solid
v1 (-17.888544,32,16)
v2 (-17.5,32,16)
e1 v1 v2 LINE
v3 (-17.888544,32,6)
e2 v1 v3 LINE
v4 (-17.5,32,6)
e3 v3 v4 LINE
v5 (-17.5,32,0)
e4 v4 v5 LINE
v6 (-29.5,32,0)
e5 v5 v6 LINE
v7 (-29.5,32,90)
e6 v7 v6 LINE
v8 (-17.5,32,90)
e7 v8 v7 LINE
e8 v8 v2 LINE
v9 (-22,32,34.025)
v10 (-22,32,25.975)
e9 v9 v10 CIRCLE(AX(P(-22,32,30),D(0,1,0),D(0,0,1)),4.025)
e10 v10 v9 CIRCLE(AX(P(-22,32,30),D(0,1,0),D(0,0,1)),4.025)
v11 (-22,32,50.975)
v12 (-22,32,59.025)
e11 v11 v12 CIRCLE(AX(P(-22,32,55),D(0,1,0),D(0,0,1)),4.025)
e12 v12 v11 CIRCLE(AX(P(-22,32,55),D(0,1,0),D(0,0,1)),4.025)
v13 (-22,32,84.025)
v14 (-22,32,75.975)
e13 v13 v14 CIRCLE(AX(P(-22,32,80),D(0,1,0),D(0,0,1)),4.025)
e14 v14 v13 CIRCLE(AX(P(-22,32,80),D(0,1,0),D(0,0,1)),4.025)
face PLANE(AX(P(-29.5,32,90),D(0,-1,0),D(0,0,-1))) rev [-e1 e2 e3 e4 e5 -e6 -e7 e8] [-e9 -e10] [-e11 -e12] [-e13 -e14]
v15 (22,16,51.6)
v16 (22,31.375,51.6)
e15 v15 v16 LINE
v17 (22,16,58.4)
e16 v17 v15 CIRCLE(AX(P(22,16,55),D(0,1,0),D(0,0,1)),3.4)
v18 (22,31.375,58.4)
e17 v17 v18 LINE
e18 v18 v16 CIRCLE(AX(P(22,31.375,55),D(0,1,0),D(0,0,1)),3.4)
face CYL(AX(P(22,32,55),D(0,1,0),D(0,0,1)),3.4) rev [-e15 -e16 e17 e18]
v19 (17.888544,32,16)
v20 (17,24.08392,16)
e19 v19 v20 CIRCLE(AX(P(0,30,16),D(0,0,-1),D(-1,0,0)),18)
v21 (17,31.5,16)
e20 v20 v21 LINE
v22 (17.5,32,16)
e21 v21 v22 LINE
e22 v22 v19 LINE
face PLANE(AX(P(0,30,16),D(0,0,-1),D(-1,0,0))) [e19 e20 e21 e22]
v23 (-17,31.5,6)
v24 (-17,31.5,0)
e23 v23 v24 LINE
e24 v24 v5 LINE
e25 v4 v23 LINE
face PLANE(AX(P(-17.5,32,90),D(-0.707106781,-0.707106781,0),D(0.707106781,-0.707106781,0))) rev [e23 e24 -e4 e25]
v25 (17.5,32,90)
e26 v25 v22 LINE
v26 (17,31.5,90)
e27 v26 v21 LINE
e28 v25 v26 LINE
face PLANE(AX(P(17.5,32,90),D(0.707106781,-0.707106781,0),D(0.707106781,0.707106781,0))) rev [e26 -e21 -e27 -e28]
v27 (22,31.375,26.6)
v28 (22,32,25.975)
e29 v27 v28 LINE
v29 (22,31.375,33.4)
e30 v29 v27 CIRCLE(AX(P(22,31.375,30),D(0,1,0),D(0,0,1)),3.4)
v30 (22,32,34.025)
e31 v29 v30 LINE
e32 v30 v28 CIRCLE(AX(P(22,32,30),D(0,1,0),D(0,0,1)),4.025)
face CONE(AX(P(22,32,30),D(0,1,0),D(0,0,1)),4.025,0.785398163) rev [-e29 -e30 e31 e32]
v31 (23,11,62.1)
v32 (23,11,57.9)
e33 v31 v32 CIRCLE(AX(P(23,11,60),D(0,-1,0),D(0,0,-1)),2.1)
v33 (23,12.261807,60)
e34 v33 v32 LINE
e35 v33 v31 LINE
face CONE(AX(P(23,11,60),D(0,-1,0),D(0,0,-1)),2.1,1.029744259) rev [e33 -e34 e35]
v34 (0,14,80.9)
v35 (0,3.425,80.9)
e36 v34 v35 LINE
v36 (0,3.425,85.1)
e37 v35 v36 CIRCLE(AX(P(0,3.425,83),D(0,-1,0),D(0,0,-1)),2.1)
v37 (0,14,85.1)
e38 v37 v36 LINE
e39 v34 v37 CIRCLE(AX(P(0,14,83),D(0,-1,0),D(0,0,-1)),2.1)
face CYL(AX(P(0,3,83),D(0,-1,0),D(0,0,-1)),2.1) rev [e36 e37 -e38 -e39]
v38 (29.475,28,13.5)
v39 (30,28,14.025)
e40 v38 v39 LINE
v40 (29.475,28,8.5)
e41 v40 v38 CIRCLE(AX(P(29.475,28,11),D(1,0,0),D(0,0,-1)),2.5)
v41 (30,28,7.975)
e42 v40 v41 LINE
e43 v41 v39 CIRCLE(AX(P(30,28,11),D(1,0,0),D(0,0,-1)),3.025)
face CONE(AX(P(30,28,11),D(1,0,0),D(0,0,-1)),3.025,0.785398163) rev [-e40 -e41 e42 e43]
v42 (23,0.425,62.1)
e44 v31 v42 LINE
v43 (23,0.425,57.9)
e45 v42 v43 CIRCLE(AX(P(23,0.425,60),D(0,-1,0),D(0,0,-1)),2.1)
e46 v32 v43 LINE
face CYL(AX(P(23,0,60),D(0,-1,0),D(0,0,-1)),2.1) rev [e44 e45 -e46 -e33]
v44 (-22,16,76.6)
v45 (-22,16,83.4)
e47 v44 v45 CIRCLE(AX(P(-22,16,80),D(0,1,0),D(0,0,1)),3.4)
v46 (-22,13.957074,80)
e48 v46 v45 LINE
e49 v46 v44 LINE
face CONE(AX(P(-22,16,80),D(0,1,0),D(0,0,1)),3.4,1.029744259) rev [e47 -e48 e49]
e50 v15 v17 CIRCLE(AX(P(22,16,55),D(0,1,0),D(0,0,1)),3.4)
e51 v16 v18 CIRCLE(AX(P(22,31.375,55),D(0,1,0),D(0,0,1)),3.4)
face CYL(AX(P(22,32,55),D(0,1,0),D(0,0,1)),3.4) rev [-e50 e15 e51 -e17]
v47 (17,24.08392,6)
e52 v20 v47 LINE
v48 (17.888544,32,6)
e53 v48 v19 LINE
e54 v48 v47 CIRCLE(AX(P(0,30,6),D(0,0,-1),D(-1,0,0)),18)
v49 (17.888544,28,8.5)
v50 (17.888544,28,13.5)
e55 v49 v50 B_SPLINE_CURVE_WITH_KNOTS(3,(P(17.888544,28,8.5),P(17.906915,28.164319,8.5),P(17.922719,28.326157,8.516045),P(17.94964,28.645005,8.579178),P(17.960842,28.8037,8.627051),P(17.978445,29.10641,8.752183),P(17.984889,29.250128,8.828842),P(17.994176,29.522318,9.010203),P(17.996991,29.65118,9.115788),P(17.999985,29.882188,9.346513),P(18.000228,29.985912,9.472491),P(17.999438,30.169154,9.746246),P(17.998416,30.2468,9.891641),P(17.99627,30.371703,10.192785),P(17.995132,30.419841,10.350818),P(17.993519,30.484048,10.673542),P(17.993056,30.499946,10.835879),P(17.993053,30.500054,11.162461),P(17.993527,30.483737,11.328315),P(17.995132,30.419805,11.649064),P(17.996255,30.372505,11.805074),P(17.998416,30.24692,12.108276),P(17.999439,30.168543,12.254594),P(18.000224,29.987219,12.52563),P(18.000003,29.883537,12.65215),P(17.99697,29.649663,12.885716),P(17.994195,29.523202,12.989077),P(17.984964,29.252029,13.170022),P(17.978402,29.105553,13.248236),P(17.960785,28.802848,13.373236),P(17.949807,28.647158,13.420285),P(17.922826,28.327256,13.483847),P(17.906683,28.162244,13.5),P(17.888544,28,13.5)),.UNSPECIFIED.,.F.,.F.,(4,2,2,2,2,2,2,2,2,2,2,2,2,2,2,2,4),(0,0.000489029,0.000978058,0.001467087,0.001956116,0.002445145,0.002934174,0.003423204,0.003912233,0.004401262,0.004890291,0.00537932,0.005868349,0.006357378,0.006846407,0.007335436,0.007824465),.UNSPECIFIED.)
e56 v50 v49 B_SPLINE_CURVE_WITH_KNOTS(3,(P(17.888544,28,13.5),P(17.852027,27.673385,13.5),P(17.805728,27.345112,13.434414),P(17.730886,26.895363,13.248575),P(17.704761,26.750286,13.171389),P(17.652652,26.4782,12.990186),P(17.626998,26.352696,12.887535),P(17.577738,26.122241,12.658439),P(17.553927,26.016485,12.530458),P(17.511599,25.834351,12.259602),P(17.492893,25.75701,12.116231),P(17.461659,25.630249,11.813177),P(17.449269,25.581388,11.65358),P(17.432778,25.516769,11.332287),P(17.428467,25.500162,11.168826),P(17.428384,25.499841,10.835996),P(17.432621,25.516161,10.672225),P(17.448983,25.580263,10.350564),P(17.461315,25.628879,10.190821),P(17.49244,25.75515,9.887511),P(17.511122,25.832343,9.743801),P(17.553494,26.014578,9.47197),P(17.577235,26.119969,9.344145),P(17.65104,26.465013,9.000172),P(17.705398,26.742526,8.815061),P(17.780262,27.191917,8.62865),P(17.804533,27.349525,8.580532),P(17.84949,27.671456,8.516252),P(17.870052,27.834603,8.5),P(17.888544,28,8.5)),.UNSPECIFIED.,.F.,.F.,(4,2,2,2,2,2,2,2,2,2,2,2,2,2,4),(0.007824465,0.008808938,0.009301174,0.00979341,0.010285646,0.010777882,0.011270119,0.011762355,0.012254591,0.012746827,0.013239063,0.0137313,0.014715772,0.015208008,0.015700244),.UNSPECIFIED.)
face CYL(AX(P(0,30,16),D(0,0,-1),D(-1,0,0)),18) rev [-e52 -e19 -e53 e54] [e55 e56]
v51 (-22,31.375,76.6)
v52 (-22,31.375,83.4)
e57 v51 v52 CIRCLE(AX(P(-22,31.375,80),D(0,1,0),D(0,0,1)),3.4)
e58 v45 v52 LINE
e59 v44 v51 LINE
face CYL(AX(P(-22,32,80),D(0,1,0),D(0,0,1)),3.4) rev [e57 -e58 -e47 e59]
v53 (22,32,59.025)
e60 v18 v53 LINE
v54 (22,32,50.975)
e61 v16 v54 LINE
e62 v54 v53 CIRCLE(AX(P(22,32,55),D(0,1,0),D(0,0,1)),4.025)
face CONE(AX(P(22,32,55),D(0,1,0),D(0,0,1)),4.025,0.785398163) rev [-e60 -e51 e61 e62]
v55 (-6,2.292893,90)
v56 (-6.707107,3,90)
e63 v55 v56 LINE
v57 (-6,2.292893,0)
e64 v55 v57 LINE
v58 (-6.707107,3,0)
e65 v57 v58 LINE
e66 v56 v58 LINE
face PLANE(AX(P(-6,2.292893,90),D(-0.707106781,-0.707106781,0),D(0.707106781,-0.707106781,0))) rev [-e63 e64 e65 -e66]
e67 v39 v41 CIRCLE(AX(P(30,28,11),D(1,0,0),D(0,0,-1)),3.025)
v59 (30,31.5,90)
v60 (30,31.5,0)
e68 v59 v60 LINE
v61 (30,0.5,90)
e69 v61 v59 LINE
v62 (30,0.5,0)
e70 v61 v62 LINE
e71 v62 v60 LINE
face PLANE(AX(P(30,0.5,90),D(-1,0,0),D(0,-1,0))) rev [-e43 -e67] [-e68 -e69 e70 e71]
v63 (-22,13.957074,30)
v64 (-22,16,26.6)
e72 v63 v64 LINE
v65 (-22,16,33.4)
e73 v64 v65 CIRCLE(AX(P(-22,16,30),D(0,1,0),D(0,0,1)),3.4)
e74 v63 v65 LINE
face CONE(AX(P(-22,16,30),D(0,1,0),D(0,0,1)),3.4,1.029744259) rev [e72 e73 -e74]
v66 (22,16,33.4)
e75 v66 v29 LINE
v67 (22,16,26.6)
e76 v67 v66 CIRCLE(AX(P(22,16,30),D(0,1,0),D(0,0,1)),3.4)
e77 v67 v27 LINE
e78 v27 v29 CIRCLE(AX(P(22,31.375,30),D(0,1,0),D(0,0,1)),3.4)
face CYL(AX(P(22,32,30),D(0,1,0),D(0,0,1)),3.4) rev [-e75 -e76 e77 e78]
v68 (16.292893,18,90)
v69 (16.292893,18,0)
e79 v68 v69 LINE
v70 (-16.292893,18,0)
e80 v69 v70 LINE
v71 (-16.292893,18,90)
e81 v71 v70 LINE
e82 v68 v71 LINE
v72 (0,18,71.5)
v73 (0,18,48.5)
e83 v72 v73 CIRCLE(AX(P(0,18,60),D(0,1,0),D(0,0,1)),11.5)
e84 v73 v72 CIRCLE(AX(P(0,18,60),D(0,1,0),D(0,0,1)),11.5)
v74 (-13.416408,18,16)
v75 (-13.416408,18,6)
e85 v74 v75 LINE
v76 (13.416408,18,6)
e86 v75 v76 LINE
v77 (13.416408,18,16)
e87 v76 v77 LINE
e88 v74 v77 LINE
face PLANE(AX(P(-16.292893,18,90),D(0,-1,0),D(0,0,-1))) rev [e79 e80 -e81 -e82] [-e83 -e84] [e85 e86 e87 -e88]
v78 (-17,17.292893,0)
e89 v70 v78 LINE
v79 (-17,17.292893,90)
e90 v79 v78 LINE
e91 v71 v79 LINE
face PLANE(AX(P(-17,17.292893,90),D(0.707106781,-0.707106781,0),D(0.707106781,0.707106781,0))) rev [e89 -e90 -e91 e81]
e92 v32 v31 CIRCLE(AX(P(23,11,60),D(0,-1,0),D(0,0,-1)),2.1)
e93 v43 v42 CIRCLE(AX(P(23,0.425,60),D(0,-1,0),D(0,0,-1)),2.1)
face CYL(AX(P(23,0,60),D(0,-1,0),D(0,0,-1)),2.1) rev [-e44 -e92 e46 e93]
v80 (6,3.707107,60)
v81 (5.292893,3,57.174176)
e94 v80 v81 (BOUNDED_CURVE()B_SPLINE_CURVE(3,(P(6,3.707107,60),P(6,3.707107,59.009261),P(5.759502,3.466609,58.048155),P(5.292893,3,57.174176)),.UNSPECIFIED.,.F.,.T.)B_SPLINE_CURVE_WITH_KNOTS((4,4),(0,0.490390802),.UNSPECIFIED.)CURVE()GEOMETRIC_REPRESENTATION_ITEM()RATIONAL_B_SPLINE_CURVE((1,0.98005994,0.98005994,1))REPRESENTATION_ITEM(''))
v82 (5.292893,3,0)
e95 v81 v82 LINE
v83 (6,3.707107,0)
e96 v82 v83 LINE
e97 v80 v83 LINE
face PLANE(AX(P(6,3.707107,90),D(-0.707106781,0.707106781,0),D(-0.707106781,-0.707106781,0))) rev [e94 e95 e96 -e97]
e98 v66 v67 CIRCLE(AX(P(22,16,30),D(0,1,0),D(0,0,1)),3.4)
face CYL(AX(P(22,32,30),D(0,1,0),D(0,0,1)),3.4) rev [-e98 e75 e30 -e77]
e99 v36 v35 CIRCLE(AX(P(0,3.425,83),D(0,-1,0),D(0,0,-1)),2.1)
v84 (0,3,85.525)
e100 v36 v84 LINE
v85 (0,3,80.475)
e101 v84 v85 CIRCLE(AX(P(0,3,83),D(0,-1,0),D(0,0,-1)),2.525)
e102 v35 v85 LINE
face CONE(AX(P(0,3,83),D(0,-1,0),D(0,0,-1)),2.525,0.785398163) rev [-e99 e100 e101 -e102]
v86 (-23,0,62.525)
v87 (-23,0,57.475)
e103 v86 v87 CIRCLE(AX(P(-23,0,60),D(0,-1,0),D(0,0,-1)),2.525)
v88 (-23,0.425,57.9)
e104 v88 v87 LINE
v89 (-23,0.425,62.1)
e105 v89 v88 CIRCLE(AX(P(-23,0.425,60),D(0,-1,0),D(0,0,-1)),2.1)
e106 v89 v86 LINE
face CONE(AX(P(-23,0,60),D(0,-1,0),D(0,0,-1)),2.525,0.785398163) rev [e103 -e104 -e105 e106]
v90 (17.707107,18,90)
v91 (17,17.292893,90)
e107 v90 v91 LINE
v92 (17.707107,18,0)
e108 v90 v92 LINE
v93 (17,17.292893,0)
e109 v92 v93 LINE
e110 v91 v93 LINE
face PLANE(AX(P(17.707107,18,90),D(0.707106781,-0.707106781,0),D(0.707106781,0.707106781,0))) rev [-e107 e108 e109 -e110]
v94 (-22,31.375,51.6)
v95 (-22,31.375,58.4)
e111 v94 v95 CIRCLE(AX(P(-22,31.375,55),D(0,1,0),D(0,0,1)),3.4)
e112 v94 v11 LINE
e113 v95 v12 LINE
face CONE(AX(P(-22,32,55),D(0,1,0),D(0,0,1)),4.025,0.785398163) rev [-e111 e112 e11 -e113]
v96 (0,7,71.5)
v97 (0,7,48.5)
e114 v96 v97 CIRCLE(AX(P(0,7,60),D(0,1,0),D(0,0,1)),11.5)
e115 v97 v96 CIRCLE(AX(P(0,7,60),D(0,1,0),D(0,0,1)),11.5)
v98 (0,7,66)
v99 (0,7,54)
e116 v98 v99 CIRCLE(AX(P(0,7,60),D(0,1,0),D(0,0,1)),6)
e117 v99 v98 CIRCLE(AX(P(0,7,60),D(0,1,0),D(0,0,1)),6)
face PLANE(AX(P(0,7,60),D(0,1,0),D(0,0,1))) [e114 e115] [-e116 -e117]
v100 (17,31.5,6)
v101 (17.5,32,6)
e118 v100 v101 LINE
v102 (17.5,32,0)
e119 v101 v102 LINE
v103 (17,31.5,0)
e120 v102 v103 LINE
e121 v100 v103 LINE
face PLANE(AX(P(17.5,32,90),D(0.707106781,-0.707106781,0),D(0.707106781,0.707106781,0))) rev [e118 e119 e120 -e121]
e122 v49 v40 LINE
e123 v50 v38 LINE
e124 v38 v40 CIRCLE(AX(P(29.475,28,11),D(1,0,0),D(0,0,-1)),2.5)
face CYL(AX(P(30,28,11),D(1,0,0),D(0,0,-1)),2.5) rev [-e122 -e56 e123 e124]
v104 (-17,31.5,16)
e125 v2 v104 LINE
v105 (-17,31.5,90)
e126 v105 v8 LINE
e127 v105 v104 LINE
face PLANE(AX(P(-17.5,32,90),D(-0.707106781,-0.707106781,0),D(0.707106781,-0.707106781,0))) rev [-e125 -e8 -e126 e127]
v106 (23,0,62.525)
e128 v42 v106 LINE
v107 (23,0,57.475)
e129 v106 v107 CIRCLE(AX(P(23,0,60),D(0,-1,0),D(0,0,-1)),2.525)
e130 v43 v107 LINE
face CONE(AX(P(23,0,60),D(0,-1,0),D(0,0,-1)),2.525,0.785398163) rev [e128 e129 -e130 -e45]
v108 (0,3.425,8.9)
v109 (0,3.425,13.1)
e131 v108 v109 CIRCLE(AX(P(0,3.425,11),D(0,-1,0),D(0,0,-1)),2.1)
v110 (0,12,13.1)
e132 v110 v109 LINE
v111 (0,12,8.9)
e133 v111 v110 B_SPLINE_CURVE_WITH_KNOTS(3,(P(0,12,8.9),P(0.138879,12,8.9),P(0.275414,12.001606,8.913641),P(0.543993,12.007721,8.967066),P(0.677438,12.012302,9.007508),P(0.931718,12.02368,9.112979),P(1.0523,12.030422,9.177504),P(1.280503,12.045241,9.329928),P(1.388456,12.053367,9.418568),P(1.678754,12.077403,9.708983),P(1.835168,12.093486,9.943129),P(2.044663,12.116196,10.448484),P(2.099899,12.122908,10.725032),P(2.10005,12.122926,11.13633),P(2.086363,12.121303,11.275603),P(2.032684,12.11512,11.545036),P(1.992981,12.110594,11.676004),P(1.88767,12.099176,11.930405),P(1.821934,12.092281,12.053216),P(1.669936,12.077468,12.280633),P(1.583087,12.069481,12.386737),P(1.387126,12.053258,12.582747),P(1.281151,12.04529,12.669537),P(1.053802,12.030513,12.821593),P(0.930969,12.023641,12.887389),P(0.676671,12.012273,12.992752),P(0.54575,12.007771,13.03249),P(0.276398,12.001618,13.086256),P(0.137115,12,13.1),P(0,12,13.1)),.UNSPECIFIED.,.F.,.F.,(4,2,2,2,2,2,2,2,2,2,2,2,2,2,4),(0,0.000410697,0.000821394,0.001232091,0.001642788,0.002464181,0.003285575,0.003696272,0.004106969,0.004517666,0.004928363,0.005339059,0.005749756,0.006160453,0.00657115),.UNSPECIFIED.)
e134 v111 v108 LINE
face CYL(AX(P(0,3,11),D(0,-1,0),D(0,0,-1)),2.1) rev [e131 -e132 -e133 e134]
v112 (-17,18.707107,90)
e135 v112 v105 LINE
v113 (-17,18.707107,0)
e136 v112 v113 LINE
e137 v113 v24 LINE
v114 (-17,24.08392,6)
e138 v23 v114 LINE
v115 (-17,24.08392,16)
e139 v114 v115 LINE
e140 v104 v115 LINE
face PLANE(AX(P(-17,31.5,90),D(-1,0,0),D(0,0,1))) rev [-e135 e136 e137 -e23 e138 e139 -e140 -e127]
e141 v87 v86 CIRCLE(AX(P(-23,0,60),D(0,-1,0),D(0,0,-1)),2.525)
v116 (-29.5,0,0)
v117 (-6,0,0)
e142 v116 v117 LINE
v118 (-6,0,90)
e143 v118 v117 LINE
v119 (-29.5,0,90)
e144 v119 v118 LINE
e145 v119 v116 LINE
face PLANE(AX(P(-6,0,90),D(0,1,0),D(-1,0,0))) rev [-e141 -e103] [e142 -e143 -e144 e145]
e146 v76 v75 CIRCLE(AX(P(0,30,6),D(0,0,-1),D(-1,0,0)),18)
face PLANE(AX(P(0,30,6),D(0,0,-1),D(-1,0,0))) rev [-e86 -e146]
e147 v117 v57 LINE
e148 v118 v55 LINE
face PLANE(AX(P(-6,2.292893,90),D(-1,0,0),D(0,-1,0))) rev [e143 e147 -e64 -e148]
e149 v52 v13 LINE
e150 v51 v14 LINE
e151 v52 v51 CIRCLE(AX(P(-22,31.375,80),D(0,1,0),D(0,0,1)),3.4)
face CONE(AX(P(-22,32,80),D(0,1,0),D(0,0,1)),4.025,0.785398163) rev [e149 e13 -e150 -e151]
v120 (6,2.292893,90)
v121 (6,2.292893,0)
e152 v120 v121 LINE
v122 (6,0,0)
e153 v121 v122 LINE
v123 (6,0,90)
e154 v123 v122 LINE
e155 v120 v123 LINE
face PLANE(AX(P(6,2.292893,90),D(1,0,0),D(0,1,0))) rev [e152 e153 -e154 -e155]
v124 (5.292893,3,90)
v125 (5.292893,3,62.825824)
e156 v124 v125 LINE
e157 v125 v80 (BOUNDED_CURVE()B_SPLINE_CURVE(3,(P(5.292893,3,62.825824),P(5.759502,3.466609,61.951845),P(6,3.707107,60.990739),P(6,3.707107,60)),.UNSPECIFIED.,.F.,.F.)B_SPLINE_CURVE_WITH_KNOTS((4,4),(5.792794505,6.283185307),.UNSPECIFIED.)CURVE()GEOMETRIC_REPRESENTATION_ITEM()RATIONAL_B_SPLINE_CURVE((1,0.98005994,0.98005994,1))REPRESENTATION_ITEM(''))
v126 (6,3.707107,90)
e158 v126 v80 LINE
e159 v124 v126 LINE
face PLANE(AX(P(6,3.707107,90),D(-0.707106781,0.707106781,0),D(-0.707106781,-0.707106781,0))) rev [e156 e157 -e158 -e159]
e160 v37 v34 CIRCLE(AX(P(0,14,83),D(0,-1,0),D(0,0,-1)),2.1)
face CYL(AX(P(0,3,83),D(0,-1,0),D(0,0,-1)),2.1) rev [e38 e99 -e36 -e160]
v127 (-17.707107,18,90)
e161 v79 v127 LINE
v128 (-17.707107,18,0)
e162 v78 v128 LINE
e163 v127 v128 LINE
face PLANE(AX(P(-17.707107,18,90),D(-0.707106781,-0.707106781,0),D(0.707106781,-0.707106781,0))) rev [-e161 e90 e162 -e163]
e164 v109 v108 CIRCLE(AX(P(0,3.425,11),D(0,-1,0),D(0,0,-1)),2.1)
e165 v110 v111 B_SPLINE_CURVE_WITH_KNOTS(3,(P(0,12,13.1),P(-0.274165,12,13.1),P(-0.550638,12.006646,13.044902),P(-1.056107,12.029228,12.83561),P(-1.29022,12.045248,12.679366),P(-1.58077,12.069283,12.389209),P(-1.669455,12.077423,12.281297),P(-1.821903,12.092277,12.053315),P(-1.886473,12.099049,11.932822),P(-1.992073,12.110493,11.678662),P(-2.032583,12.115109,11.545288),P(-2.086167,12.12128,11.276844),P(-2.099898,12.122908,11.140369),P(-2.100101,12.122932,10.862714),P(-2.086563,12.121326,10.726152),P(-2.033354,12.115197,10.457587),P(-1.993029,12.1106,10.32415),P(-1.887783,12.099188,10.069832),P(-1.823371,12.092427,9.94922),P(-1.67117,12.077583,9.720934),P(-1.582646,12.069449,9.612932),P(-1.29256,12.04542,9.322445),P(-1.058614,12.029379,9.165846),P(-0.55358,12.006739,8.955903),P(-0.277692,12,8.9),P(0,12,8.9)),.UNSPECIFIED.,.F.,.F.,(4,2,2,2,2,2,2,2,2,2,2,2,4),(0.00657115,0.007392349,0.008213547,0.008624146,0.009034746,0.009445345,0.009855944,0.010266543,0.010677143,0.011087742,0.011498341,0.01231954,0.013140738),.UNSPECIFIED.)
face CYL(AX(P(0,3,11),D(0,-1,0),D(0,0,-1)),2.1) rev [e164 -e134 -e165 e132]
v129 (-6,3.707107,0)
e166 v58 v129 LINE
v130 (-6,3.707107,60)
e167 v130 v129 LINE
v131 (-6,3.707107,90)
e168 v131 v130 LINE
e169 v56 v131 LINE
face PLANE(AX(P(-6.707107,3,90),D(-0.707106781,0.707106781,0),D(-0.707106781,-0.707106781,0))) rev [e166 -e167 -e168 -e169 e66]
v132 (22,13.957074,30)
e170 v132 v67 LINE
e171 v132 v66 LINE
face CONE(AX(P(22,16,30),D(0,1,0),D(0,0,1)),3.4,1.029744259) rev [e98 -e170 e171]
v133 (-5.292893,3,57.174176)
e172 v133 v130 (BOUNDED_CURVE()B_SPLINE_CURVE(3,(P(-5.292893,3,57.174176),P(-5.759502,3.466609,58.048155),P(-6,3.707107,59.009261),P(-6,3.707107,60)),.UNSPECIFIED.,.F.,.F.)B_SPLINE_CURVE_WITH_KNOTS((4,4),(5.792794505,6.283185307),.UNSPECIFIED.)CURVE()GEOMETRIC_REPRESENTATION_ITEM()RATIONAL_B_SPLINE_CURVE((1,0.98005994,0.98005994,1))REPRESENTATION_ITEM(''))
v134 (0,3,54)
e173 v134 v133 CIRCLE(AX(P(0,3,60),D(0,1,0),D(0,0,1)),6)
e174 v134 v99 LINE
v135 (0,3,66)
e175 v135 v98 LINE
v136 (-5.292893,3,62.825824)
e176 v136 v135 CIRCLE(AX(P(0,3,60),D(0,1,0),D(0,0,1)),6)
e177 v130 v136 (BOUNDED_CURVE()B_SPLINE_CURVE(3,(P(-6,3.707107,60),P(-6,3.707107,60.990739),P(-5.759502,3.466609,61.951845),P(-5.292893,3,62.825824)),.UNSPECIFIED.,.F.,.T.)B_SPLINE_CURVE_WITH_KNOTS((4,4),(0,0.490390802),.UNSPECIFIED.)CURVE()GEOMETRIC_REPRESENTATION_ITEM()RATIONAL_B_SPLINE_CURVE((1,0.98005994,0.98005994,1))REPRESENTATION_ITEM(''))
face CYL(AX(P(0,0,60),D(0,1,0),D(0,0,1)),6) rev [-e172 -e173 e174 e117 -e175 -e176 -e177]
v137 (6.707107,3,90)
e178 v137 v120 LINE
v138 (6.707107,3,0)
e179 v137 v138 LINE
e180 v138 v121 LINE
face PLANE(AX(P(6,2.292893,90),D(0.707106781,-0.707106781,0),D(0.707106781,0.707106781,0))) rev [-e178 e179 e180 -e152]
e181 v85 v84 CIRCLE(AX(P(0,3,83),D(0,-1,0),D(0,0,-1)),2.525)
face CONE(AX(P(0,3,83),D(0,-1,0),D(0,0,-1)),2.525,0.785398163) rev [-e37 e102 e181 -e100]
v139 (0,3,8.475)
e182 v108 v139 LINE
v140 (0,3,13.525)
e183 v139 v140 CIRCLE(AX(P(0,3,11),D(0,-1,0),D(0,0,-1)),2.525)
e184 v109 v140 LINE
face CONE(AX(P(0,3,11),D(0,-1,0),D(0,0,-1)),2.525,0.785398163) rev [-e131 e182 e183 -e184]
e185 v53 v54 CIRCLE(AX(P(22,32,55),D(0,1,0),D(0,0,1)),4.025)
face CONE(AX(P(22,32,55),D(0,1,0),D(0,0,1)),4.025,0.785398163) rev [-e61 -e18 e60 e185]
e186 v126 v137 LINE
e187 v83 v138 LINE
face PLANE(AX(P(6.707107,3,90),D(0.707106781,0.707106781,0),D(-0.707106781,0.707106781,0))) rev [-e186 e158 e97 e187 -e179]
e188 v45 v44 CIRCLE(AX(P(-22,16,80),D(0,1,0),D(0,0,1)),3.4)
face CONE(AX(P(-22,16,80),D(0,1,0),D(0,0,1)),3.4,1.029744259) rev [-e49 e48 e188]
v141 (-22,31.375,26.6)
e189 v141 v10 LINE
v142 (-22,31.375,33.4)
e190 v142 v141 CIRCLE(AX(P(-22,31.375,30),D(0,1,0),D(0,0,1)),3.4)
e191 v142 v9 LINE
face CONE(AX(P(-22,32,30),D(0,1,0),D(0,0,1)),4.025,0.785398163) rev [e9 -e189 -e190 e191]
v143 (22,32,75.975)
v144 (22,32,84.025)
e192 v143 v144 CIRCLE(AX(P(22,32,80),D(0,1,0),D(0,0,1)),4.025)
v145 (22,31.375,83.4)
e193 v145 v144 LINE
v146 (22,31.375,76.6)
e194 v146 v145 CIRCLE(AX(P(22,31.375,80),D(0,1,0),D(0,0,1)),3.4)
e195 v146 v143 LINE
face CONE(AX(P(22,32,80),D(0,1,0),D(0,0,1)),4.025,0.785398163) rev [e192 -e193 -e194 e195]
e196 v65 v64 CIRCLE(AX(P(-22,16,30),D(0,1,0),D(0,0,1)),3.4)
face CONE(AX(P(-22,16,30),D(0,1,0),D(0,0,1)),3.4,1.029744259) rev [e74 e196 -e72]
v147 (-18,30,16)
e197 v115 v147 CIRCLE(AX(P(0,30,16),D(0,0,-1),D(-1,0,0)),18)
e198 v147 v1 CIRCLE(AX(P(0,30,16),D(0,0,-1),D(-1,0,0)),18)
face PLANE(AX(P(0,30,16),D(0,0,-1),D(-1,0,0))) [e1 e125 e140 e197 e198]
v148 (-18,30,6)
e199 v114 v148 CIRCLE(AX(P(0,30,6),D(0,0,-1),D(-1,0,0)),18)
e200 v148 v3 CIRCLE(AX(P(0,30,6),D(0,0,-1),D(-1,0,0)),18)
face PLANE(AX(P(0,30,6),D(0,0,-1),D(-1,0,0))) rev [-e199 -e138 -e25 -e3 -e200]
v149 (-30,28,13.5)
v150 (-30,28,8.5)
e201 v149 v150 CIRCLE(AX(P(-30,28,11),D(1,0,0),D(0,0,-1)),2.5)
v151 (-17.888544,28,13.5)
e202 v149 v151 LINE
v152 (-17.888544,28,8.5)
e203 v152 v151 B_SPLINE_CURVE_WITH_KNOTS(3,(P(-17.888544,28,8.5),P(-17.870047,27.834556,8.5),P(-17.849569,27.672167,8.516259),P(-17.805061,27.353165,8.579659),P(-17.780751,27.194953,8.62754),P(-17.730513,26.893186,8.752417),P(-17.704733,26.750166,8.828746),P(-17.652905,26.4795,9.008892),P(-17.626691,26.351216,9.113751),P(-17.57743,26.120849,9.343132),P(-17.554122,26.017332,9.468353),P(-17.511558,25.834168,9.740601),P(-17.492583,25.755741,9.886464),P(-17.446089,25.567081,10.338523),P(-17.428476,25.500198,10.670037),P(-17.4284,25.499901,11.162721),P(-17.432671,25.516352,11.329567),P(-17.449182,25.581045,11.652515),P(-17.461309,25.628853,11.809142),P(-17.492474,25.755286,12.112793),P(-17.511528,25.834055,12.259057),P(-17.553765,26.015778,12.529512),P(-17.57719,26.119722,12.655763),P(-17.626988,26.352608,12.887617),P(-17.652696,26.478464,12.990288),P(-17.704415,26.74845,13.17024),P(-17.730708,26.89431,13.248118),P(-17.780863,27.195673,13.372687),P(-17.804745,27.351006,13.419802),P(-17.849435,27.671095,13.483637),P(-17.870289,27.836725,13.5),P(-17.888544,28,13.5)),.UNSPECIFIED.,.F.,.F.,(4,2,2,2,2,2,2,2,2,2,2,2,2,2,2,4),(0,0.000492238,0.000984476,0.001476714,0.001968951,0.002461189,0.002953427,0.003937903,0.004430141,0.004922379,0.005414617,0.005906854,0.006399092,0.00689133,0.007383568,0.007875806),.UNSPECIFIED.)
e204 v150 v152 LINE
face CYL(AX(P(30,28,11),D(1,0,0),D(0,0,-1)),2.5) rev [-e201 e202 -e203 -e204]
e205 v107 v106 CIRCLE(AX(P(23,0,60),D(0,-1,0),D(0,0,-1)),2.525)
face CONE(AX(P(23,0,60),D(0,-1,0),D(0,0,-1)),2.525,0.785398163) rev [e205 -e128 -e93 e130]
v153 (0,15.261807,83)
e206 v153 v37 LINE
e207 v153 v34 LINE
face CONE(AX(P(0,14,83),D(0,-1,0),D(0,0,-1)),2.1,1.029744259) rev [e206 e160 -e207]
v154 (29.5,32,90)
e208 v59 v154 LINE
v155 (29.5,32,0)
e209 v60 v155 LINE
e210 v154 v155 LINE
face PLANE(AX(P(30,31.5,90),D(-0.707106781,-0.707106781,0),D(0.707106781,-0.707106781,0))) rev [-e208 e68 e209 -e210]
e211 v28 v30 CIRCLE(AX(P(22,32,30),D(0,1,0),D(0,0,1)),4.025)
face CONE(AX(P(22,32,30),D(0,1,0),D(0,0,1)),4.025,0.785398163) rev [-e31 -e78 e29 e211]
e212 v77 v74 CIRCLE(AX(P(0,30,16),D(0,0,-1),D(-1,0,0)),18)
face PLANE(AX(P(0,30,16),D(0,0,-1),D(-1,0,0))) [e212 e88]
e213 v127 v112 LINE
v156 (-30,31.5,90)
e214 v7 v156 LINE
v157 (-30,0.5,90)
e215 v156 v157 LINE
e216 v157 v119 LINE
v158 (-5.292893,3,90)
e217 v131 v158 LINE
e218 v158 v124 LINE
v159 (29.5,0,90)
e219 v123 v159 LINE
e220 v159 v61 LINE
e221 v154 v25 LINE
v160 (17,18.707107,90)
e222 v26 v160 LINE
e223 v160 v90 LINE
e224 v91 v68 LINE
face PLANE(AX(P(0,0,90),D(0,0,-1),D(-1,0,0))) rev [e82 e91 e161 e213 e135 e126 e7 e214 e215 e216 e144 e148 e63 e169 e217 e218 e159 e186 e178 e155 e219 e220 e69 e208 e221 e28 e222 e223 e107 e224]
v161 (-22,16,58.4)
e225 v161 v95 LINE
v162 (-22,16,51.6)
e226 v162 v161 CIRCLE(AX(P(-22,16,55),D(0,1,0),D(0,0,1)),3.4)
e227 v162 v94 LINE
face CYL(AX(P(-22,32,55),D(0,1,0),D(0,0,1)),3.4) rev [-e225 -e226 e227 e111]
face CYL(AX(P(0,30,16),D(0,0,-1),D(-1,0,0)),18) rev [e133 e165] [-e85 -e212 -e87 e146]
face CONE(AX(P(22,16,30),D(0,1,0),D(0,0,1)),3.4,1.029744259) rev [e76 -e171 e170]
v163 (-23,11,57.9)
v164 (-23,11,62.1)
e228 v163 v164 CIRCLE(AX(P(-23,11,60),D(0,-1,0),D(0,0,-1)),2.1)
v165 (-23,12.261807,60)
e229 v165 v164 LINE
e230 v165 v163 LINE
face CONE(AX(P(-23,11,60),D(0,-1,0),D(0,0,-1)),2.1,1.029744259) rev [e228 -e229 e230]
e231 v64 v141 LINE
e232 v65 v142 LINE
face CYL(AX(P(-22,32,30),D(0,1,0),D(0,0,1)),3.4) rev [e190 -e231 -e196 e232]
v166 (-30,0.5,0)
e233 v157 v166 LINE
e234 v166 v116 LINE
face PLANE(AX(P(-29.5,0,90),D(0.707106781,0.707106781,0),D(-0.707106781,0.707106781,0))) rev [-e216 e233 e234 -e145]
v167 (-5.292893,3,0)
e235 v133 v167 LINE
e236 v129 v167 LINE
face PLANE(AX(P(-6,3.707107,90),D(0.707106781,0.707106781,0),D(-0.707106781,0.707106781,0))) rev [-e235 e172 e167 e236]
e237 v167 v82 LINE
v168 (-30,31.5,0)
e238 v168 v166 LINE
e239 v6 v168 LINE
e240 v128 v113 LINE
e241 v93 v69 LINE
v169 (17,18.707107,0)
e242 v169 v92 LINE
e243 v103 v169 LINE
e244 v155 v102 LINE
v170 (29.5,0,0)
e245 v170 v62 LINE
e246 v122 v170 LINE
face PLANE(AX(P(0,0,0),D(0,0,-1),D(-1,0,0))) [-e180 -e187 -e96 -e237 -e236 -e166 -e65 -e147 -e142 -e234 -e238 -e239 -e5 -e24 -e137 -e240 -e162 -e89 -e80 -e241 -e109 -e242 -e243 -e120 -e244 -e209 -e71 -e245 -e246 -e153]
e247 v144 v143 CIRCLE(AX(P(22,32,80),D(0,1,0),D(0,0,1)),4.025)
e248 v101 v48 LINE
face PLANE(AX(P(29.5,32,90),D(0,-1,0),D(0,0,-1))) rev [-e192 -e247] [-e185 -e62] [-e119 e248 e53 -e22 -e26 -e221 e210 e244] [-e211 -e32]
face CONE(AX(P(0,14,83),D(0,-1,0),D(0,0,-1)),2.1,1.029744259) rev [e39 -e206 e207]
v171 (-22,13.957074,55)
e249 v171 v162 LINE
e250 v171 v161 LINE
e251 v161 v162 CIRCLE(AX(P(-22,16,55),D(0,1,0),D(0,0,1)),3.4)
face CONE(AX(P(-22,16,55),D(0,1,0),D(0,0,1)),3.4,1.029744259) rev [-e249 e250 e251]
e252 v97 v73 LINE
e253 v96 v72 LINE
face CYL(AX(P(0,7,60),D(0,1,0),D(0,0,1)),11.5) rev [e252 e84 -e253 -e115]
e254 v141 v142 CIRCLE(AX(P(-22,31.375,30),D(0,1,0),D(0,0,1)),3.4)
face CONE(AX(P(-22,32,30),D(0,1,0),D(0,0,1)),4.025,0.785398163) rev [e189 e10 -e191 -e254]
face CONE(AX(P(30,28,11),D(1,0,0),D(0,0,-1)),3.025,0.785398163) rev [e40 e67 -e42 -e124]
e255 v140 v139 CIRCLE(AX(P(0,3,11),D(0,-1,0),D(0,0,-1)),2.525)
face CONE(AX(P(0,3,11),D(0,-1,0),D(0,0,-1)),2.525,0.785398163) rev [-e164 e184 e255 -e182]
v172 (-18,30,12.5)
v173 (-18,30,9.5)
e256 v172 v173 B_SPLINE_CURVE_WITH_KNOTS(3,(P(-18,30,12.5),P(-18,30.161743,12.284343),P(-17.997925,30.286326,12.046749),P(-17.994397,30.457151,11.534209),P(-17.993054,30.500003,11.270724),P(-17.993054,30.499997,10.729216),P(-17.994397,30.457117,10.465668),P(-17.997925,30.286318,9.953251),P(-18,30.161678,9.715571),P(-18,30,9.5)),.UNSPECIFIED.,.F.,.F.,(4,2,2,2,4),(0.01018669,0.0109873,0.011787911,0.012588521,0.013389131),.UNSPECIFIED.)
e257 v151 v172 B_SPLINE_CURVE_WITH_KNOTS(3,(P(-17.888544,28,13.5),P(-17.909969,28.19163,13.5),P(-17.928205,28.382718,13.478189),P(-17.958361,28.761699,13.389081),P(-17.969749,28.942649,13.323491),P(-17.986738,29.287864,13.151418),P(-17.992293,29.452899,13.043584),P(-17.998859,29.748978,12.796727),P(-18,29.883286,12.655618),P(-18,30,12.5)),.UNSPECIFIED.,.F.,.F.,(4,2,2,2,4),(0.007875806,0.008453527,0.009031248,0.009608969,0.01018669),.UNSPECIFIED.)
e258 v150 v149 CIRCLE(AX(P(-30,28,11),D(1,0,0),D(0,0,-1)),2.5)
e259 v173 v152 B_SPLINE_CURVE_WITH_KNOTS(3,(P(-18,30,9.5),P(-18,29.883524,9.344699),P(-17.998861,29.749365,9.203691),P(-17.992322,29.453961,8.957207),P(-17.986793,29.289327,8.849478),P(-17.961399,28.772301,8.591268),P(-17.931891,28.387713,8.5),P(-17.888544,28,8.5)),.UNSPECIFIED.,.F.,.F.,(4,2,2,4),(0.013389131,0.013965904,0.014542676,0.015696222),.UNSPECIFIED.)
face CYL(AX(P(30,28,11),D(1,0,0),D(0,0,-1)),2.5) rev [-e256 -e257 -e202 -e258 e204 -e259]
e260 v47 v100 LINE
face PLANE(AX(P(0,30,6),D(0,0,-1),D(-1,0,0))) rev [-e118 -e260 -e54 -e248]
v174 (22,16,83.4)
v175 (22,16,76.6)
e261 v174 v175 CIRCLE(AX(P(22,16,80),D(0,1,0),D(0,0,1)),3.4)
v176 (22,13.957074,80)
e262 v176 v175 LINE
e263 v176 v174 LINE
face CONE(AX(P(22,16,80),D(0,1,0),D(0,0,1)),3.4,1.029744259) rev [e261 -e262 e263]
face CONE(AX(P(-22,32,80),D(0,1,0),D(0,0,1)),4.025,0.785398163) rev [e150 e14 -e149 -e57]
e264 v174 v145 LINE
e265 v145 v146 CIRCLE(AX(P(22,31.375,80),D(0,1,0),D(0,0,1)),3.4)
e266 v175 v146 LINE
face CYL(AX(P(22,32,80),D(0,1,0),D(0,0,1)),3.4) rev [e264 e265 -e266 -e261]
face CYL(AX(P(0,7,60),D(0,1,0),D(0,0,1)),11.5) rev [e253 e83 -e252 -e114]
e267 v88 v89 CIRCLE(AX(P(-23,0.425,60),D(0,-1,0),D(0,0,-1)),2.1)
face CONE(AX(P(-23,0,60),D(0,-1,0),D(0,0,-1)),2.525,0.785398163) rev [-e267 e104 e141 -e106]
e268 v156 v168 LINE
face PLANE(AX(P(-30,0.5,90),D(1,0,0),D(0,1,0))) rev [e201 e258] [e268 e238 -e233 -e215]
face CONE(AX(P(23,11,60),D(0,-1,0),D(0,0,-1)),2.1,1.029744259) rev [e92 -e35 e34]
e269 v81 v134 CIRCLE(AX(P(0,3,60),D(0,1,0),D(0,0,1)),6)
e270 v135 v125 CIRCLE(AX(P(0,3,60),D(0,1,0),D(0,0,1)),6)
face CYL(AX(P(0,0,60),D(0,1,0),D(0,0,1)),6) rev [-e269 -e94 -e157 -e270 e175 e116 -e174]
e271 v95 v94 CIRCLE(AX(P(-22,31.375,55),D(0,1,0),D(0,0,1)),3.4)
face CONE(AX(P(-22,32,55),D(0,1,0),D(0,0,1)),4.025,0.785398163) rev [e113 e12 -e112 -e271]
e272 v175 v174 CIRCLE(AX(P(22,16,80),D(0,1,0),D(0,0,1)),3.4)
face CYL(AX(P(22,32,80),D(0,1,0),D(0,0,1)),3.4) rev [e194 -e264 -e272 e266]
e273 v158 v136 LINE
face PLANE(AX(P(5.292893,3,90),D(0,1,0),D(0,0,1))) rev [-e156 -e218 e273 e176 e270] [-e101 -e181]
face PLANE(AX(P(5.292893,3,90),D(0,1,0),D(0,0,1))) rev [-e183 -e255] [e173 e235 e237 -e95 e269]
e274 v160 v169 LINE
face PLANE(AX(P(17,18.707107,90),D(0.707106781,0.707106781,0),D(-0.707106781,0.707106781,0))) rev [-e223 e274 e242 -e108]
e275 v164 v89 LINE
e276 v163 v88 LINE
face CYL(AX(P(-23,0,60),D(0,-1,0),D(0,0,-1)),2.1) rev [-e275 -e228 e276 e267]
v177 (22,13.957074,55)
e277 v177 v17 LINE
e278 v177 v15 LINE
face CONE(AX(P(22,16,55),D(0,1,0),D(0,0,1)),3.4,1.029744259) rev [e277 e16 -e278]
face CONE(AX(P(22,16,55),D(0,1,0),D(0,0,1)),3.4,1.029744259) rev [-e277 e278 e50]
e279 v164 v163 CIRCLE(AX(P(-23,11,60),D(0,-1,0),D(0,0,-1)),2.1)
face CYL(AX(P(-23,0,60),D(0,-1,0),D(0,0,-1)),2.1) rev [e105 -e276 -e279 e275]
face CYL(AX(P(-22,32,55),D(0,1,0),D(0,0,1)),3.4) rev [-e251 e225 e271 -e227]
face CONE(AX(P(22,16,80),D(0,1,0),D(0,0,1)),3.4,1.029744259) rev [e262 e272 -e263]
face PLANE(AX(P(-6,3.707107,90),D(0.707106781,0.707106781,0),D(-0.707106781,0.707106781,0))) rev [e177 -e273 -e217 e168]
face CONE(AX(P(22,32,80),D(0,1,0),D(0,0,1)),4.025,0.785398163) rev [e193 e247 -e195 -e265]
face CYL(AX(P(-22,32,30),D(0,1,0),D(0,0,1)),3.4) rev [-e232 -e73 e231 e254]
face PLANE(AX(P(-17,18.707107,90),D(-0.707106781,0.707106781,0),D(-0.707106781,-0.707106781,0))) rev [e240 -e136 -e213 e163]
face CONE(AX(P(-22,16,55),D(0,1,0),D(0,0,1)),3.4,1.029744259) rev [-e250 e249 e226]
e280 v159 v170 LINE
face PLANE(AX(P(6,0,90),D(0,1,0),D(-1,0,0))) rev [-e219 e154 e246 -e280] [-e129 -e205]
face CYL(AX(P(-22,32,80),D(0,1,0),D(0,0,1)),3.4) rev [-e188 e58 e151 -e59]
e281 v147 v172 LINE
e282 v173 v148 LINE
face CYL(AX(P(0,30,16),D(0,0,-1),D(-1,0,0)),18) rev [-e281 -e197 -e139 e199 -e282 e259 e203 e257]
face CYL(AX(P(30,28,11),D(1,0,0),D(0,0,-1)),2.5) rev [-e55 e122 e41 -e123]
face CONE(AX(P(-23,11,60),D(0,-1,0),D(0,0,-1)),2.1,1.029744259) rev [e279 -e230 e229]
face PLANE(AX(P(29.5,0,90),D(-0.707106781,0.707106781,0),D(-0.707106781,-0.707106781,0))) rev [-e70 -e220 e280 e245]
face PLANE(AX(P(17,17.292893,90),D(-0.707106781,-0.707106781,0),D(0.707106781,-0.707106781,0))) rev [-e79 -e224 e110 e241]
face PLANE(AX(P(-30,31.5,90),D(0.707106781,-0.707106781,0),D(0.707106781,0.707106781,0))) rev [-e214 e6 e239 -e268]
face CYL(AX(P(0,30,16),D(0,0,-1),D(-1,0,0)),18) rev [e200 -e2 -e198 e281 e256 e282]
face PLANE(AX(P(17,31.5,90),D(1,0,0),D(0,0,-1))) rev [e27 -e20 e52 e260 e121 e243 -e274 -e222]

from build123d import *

# Parameters (mm, degrees)
BOSS_EXTRUDE1_DEPTH                   = 90
SKETCH2_R                             = 11.5
CUT_EXTRUDE1_DEPTH                    = 11
SKETCH3_R                             = 6
CUT_EXTRUDE2_DEPTH                    = 99.107084352
CUT_EXTRUDE3_START                    = -6
SKETCH4_R                             = 18
CUT_EXTRUDE3_DEPTH                    = 10
M8_TAPPED_HOLE1_D                     = 6.8
M8_TAPPED_HOLE1_DEPTH                 = 16
M8_TAPPED_HOLE1_CSINK_D               = 8.05
M8_TAPPED_HOLE1_CSINK_ANGLE           = 90
M8_TAPPED_HOLE1_TIP                   = 2.042926105
M6_TAPPED_HOLE1_D                     = 5
M6_TAPPED_HOLE1_CSINK_D               = 6.05
M6_TAPPED_HOLE1_CSINK_ANGLE           = 90
M5_TAPPED_HOLE1_D                     = 4.2
M5_TAPPED_HOLE1_CSINK_D               = 5.05
M5_TAPPED_HOLE1_CSINK_ANGLE           = 90
M5_TAPPED_HOLE2_D                     = 4.2
M5_TAPPED_HOLE2_DEPTH                 = 11
M5_TAPPED_HOLE2_CSINK_D               = 5.05
M5_TAPPED_HOLE2_CSINK_ANGLE           = 90
M5_TAPPED_HOLE2_TIP                   = 1.2618073
M5_TAPPED_HOLE2_ON_FACE_2_D           = 4.2
M5_TAPPED_HOLE2_ON_FACE_2_DEPTH       = 11
M5_TAPPED_HOLE2_ON_FACE_2_CSINK_D     = 5.05
M5_TAPPED_HOLE2_ON_FACE_2_CSINK_ANGLE = 90
M5_TAPPED_HOLE2_ON_FACE_2_TIP         = 1.2618073


with BuildPart() as part:
    # Sketch1 → Boss-Extrude1 (new body)
    with BuildSketch(Plane.XY):
        Polygon((-6, 0), (-29.5, 0), (-30, 0.5), (-30, 31.5), (-29.5, 32), (-17.5, 32), (-17, 31.5), (-17, 18.707106781), (-17.707106781, 18), (-17, 17.292893219), (-16.292893219, 18), (16.292893219, 18), (17, 17.292893219), (17.707106781, 18), (17, 18.707106781), (17, 31.5), (17.5, 32), (29.5, 32), (30, 31.5), (30, 0.5), (29.5, 0), (6, 0), (6, 2.292893219), (6.707106781, 3), (6, 3.707106781), (5.292893219, 3), (-5.292893219, 3), (-6, 3.707106781), (-6.707106781, 3), (-6, 2.292893219), align=None)
    extrude(amount=BOSS_EXTRUDE1_DEPTH)

    # Sketch2 → Cut-Extrude1 (cut)
    with BuildSketch(Plane(origin=(0, 18, 0), x_dir=(1, 0, 0), z_dir=(0, 1, 0))):
        with Locations(Location((0, -60, 0), (0, 0, 270))):
            Circle(SKETCH2_R)
    extrude(amount=-CUT_EXTRUDE1_DEPTH, mode=Mode.SUBTRACT)

    # Sketch3 → Cut-Extrude2 (cut, through all)
    with BuildSketch(Plane(origin=(0, 7, 0), x_dir=(1, 0, 0), z_dir=(0, 1, 0))):
        with Locations(Location((0, -60, 0), (0, 0, 270))):
            Circle(SKETCH3_R)
    extrude(amount=-CUT_EXTRUDE2_DEPTH, mode=Mode.SUBTRACT)

    # Sketch4 → Cut-Extrude3 (cut)
    with BuildSketch(Plane(origin=(0, 0, 0), x_dir=(-1, 0, 0), z_dir=(0, 0, -1)).offset(CUT_EXTRUDE3_START)):
        with Locations((0, 30)):
            Circle(SKETCH4_R)
    extrude(amount=-CUT_EXTRUDE3_DEPTH, mode=Mode.SUBTRACT)

    # M8 Tapped Hole1
    with Locations(Plane(origin=(-22, 32, 30), x_dir=(0, 0, 1), z_dir=(0, 1, 0))):
        with Locations((0, 0), (25, 0), (50, 0), (0, 44), (25, 44), (50, 44)):
            CounterSinkHole(M8_TAPPED_HOLE1_D / 2, M8_TAPPED_HOLE1_CSINK_D / 2, depth=M8_TAPPED_HOLE1_DEPTH, counter_sink_angle=M8_TAPPED_HOLE1_CSINK_ANGLE)
            with Locations((0, 0, -(M8_TAPPED_HOLE1_DEPTH + M8_TAPPED_HOLE1_TIP / 2))):  # 118° drill point
                Cone(0, M8_TAPPED_HOLE1_D / 2, M8_TAPPED_HOLE1_TIP, mode=Mode.SUBTRACT)

    # M6 Tapped Hole1 (through all)
    with Locations(Plane(origin=(30, 28, 11), x_dir=(0, 1, 0), z_dir=(1, 0, 0))):
        with Locations((0, 0)):
            CounterSinkHole(M6_TAPPED_HOLE1_D / 2, M6_TAPPED_HOLE1_CSINK_D / 2, counter_sink_angle=M6_TAPPED_HOLE1_CSINK_ANGLE)

    # M5 Tapped Hole1 (through all)
    with Locations(Plane(origin=(0, 3, 11), x_dir=(0, 0, -1), z_dir=(0, -1, 0))):
        with Locations((0, 0)):
            CounterSinkHole(M5_TAPPED_HOLE1_D / 2, M5_TAPPED_HOLE1_CSINK_D / 2, counter_sink_angle=M5_TAPPED_HOLE1_CSINK_ANGLE)

    # M5 Tapped Hole2
    with Locations(Plane(origin=(0, 3, 83), x_dir=(0, 0, -1), z_dir=(0, -1, 0))):
        with Locations((0, 0)):
            CounterSinkHole(M5_TAPPED_HOLE2_D / 2, M5_TAPPED_HOLE2_CSINK_D / 2, depth=M5_TAPPED_HOLE2_DEPTH, counter_sink_angle=M5_TAPPED_HOLE2_CSINK_ANGLE)
            with Locations((0, 0, -(M5_TAPPED_HOLE2_DEPTH + M5_TAPPED_HOLE2_TIP / 2))):  # 118° drill point
                Cone(0, M5_TAPPED_HOLE2_D / 2, M5_TAPPED_HOLE2_TIP, mode=Mode.SUBTRACT)

    # M5 Tapped Hole2 on face 2
    with Locations(Plane(origin=(23, 0, 60), x_dir=(0, 0, -1), z_dir=(0, -1, 0))):
        with Locations((0, 0), (0, -46)):
            CounterSinkHole(M5_TAPPED_HOLE2_ON_FACE_2_D / 2, M5_TAPPED_HOLE2_ON_FACE_2_CSINK_D / 2, depth=M5_TAPPED_HOLE2_ON_FACE_2_DEPTH, counter_sink_angle=M5_TAPPED_HOLE2_ON_FACE_2_CSINK_ANGLE)
            with Locations((0, 0, -(M5_TAPPED_HOLE2_ON_FACE_2_DEPTH + M5_TAPPED_HOLE2_ON_FACE_2_TIP / 2))):  # 118° drill point
                Cone(0, M5_TAPPED_HOLE2_ON_FACE_2_D / 2, M5_TAPPED_HOLE2_ON_FACE_2_TIP, mode=Mode.SUBTRACT)


solid = part.part
